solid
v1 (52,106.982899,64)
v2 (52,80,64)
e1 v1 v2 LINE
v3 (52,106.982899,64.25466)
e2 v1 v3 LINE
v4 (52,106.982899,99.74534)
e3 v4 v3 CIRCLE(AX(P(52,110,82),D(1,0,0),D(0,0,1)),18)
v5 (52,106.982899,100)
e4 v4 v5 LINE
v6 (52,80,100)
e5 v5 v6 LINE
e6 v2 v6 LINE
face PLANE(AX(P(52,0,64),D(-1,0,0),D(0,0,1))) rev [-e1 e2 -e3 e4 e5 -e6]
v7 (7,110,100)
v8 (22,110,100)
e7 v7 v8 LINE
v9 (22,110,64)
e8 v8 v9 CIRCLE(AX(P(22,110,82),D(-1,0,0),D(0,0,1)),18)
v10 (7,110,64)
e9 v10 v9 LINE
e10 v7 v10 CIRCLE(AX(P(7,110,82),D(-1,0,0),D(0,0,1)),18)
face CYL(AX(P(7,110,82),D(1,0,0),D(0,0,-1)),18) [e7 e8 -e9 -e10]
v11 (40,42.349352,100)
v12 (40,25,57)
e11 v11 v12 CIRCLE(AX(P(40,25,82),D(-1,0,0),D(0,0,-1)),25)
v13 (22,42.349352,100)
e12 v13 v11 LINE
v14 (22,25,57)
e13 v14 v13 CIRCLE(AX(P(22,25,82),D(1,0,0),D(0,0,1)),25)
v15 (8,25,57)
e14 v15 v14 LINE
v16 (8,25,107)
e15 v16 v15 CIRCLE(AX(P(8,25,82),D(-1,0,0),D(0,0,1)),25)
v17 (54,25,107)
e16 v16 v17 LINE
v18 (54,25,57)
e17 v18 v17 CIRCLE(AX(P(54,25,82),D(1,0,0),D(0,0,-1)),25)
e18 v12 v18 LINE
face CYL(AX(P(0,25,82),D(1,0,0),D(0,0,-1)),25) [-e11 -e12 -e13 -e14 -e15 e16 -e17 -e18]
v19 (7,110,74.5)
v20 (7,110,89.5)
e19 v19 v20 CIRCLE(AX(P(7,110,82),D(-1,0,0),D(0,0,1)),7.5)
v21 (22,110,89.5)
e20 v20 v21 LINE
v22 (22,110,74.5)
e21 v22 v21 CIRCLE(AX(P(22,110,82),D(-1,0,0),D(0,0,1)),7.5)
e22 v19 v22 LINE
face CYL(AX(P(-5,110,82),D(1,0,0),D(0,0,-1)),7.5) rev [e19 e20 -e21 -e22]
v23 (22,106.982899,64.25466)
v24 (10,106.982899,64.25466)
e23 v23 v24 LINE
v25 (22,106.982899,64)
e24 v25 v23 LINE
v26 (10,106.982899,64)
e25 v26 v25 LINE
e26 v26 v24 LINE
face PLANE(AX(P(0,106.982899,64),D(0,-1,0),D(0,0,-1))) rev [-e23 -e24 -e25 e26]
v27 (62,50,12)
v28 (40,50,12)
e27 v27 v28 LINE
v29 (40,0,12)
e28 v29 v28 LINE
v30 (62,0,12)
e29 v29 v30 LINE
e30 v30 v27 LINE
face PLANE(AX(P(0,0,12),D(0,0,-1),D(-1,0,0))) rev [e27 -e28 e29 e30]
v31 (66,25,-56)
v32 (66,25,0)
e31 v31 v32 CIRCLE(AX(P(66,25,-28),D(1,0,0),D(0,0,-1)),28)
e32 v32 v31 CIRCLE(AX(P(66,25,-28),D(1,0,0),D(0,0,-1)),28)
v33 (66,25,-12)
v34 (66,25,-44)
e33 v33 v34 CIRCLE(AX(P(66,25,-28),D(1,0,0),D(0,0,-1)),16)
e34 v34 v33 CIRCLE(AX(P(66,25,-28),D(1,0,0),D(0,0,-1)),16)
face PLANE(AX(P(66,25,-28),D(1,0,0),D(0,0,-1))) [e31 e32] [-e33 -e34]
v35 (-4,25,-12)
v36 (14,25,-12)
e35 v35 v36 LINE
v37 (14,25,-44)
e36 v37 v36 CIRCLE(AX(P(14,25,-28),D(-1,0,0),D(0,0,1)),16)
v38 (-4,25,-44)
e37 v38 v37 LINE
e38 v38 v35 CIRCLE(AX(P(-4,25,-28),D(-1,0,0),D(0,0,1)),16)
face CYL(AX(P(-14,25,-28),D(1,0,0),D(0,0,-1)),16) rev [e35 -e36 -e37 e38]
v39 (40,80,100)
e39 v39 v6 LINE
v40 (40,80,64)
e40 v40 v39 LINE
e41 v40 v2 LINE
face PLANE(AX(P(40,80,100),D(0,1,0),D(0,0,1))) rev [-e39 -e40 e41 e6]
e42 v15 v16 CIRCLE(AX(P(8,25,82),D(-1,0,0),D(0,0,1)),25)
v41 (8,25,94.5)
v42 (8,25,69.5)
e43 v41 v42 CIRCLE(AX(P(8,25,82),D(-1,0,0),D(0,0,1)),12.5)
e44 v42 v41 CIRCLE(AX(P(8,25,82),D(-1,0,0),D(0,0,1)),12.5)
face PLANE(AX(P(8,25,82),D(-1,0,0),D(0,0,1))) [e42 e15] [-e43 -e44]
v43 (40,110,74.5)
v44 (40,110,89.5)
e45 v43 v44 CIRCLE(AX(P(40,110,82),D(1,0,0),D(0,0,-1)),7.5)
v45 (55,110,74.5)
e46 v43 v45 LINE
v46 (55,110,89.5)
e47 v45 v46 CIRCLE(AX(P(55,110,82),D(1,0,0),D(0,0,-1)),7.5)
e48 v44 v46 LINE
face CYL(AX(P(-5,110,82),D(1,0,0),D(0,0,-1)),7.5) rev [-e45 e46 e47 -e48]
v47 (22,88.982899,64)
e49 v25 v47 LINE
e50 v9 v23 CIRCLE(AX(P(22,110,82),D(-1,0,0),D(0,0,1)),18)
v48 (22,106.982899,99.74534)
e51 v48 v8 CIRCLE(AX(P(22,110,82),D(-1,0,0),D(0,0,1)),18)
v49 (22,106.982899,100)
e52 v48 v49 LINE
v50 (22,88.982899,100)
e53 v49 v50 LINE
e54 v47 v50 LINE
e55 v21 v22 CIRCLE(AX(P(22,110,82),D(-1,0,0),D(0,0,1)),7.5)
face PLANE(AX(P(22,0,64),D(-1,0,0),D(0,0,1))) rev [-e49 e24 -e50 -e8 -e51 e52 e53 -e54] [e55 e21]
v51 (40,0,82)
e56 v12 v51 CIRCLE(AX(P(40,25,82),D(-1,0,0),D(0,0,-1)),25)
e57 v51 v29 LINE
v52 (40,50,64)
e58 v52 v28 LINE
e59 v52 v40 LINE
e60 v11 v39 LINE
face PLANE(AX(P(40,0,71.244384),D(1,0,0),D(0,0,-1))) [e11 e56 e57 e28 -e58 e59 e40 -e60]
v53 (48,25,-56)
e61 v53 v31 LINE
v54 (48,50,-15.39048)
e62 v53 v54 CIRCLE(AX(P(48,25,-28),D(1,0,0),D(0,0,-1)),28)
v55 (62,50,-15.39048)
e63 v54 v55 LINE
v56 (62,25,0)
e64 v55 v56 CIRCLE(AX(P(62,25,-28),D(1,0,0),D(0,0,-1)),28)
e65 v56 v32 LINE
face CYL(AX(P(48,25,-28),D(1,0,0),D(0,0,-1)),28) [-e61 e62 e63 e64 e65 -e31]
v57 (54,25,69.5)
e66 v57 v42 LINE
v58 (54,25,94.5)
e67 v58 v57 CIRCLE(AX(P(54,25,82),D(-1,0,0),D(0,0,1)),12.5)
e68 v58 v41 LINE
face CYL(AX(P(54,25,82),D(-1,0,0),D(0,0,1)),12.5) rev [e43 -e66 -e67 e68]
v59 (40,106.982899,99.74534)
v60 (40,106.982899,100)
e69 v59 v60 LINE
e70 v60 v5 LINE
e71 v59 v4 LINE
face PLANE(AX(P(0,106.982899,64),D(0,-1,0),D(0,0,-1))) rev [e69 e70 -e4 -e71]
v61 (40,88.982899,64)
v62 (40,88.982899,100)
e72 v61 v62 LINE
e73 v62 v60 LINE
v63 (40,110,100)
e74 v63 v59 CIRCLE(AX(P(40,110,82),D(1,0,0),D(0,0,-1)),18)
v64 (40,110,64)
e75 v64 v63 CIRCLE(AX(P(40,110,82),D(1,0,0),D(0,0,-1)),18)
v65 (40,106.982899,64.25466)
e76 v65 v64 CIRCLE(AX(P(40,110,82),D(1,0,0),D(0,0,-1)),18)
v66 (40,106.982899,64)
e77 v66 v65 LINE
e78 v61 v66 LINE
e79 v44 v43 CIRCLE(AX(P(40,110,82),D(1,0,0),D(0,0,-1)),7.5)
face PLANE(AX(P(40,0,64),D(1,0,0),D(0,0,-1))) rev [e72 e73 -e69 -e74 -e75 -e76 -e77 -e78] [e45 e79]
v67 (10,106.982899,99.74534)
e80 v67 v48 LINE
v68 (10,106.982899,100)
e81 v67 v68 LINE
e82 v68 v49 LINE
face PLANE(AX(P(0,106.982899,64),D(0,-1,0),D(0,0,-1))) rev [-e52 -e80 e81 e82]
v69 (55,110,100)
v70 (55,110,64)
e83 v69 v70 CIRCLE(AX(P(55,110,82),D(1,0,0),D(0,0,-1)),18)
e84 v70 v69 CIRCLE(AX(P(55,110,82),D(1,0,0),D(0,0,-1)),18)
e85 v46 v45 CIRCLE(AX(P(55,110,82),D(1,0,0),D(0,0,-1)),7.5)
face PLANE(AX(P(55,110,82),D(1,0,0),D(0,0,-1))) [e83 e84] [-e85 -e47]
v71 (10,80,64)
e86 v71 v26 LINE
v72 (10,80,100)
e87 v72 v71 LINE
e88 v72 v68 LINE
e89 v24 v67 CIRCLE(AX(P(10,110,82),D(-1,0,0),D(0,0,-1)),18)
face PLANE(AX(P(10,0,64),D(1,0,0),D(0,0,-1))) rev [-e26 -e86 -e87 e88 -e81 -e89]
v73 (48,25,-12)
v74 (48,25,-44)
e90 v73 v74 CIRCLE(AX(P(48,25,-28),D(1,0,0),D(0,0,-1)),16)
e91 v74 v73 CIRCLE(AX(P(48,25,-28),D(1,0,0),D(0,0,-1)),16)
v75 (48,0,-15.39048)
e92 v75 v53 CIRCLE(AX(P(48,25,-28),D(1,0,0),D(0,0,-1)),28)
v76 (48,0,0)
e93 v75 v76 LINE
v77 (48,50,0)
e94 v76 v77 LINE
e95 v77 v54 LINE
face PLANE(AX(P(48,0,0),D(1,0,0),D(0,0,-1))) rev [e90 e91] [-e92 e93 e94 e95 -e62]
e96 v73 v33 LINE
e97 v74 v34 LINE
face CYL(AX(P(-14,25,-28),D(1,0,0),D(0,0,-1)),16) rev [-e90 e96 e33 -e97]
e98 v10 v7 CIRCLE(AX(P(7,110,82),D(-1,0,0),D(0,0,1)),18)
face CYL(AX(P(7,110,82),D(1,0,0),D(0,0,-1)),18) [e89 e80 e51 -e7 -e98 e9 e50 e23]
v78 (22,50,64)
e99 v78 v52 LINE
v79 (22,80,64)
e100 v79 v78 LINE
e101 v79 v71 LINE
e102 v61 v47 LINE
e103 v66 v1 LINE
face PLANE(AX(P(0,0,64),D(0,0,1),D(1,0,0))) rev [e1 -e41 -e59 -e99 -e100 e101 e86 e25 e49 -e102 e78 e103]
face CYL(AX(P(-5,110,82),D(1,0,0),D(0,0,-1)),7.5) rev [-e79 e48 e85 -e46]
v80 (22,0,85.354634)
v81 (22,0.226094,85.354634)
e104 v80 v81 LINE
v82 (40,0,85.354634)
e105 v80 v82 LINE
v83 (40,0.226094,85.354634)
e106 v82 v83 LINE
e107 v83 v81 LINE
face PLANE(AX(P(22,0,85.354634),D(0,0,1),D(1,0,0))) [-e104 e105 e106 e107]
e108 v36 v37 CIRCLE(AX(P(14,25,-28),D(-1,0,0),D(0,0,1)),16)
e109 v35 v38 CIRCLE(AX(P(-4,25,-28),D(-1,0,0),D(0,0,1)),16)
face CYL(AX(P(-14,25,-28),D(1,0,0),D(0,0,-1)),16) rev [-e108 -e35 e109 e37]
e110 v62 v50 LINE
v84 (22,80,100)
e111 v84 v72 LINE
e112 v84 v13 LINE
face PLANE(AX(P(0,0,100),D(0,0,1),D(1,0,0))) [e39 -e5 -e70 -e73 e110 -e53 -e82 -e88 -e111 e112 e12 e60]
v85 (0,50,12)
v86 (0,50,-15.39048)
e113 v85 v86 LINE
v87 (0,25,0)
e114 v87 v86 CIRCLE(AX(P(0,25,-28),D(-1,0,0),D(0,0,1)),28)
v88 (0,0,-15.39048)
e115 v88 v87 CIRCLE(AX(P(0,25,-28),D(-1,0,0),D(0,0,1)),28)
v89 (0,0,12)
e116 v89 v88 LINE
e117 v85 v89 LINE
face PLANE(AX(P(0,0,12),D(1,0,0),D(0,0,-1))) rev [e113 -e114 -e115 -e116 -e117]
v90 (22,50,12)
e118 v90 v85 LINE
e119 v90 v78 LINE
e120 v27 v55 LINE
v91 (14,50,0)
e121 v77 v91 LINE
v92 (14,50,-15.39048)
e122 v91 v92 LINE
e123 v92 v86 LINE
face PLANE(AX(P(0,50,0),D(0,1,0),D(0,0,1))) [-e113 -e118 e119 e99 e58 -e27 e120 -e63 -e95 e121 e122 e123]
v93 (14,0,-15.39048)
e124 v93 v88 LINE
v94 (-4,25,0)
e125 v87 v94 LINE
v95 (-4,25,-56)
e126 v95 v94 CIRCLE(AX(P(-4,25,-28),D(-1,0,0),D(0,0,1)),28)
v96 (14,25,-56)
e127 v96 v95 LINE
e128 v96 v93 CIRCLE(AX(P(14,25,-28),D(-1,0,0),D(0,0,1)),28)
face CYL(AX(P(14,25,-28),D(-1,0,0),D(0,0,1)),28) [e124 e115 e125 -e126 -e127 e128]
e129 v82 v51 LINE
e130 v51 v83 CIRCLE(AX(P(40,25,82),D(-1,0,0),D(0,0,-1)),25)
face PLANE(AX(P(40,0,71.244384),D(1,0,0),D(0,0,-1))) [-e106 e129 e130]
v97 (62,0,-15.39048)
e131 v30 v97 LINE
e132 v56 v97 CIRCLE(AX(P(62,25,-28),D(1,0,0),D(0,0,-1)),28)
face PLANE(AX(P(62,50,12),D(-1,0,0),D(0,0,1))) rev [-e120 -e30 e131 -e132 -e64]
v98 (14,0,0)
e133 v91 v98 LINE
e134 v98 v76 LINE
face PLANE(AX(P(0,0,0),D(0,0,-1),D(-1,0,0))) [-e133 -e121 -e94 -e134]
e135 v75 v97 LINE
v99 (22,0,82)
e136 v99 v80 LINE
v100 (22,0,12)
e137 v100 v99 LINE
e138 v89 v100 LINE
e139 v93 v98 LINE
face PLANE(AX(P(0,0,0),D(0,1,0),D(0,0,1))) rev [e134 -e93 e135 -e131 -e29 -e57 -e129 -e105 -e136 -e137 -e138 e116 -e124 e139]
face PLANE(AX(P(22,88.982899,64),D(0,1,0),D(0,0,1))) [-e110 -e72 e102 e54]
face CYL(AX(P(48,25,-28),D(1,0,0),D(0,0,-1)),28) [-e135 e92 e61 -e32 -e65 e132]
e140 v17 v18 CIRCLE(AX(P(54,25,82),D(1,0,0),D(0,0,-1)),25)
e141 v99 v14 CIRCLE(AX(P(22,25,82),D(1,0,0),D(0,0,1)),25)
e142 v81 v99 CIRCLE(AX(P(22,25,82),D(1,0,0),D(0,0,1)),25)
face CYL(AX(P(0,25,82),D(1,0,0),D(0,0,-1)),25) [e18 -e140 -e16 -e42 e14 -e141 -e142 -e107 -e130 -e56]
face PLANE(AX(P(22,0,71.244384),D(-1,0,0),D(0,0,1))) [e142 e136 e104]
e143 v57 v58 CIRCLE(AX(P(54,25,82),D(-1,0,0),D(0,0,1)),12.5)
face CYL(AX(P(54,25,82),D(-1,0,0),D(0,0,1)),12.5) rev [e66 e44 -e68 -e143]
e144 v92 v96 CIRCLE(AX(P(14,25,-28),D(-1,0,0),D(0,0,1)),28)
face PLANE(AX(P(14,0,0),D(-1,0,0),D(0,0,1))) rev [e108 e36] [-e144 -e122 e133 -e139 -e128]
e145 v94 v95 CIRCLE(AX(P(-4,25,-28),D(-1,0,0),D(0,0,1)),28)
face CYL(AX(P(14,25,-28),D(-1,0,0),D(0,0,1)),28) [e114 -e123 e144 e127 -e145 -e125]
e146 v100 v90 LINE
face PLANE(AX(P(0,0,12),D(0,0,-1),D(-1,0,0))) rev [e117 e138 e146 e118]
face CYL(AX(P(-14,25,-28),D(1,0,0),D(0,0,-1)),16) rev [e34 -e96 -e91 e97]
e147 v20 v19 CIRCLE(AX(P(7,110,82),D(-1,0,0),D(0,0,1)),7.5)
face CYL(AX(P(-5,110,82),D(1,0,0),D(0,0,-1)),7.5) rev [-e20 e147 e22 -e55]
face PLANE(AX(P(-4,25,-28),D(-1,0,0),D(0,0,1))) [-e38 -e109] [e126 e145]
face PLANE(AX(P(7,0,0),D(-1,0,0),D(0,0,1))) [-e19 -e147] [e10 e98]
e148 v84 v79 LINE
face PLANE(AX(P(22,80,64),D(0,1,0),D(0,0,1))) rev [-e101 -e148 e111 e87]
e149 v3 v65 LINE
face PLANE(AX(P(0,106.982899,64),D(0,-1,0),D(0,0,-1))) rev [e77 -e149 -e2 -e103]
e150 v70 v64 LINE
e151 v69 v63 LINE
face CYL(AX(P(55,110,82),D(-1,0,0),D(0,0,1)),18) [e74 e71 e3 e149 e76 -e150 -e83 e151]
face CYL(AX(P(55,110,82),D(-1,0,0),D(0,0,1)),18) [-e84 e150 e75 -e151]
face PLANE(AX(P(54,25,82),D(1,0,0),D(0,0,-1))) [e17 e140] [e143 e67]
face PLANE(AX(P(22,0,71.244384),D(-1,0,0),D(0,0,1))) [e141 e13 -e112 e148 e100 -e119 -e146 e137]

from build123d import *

# Parameters (mm, degrees)
BASE_PLATE_DEPTH                = 12
EYE_BOSS_A_SKETCH_R             = 28
EYE_BOSS_A_56_DEPTH             = 14
EYE_HUB_A_SKETCH_R              = 28
EYE_HUB_A_56X4_DEPTH            = 4
EYE_WEB_A_DEPTH                 = 14
EYE_START                       = -14
EYE_BOSS_B_SKETCH_R             = 28
EYE_BOSS_B_DEPTH                = 14
EYE_HUB_B_SKETCH_R              = 28
EYE_HUB_B_56X4_DEPTH            = 4
SIDE_BOSS_SKETCH_R              = 25
SIDE_BOSS_50_DEPTH              = 62
SIDE_BOSS_FACE_CUT_A_SKETCH_R   = 25
SIDE_BOSS_FACE_CUT_A_50X8_DEPTH = 8
SIDE_BOSS_FACE_CUT_B_SKETCH_R   = 25
SIDE_BOSS_FACE_CUT_B_50X8_DEPTH = 8
SIDE_BORE_SKETCH_R              = 12.5
SIDE_BORE_25_DEPTH              = 46
EYE_BORE_SKETCH_R               = 16
EYE_BORE_32_DEPTH               = 80
CENTRAL_BODY_DEPTH              = 50
BODY_START                      = -50
BODY_SLOT_CUT_DEPTH             = 50
UPPER_LUG_A_SKETCH_R            = 18
UPPER_LUG_A_36_DEPTH            = 15
UPPER_LUG_B_SKETCH_R            = 18
UPPER_LUG_B_36_DEPTH            = 15
UPPER_CLEVIS_BODY_DEPTH         = 36
UPPER_CLEVIS_INFILL_SKETCH_W    = 18
UPPER_CLEVIS_INFILL_SKETCH_H    = 12
UPPER_CLEVIS_INFILL_DEPTH       = 36
CLEVIS_SLOT_A_SKETCH_W          = 36
CLEVIS_SLOT_A_SKETCH_H          = 18
CLEVIS_SLOT_A_DEPTH             = 12
CLEVIS_SLOT_B_SKETCH_W          = 36
CLEVIS_SLOT_B_SKETCH_H          = 18
CLEVIS_SLOT_B_DEPTH             = 12
LUG_PIN_HOLE_SKETCH_R           = 7.5
LUG_PIN_HOLE_15_DEPTH           = 60
SIDE_SLOT_CUT_DEPTH             = 60


with BuildPart() as part:
    # Base Plate Sketch → Base Plate (new body)
    with BuildSketch(Plane.XY):
        Polygon((0, 0), (14, 0), (48, 0), (62, 0), (62, 50), (0, 50), align=None)
    extrude(amount=BASE_PLATE_DEPTH)



with BuildPart() as body_2:
    # Eye Boss A Sketch → Eye Boss A _56 (new body)
    with BuildSketch(Plane(origin=(62, 0, 0), x_dir=(0, 0, -1), z_dir=(1, 0, 0))):
        with Locations((28, 25)):
            Circle(EYE_BOSS_A_SKETCH_R)
    extrude(amount=-EYE_BOSS_A_56_DEPTH)

    # Eye Hub A Sketch → Eye Hub A _56x4 (add)
    with BuildSketch(Plane(origin=(62, 0, 0), x_dir=(0, 0, -1), z_dir=(1, 0, 0))):
        with Locations((28, 25)):
            Circle(EYE_HUB_A_SKETCH_R)
    extrude(amount=EYE_HUB_A_56X4_DEPTH)


with BuildPart() as part_1:
    add(part.part)

    add(body_2.part)  # Eye Web A merges body 2
    # Eye Web A Sketch → Eye Web A (add)
    with BuildSketch(Plane(origin=(62, 0, 0), x_dir=(0, 0, -1), z_dir=(1, 0, 0))):
        with BuildLine():
            Line((15.390479787, 50), (0, 50))
            Line((0, 50), (0, 25.000000117))
            ThreePointArc((0, 25.000000117), (4.156064051, 39.678784639), (15.390479787, 50))
        make_face()
        with BuildLine():
            ThreePointArc((15.390479787, 0), (4.15606399, 10.32121546), (0, 25.000000117))
            Line((0, 25.000000117), (0, 0))
            Line((0, 0), (15.390479787, 0))
        make_face()
    extrude(amount=-EYE_WEB_A_DEPTH)

    # Eye Boss B Sketch → Eye Boss B (add)
    with BuildSketch(Plane.ZY.offset(EYE_START)):
        with Locations(Location((-28, 25, 0), (0, 0, 180))):
            Circle(EYE_BOSS_B_SKETCH_R)
        with BuildLine():
            Line((0, 25), (0, 50))
            Line((0, 50), (-15.390479787, 50))
            ThreePointArc((-15.390479787, 50), (-4.156064021, 39.678784589), (0, 25))
        make_face()
        with BuildLine():
            Line((0, 0), (0, 25))
            ThreePointArc((0, 25), (-4.156064021, 10.321215411), (-15.390479787, 0))
            Line((-15.390479787, 0), (0, 0))
        make_face()
    extrude(amount=EYE_BOSS_B_DEPTH)

    # Eye Hub B Sketch → Eye Hub B _56x4 (add)
    with BuildSketch(Plane.ZY):
        with Locations(Location((-28, 25, 0), (0, 0, 180))):
            Circle(EYE_HUB_B_SKETCH_R)
    extrude(amount=EYE_HUB_B_56X4_DEPTH)

    # Eye Bore Sketch → Eye Bore _32 (cut)
    with BuildSketch(Plane(origin=(66, 0, 0), x_dir=(0, 0, -1), z_dir=(1, 0, 0))):
        with Locations(Location((28, 25, 0), (0, 0, 180))):
            Circle(EYE_BORE_SKETCH_R)
    extrude(amount=-EYE_BORE_32_DEPTH, mode=Mode.SUBTRACT)



with BuildPart() as body_2_2:
    # Side Boss Sketch → Side Boss _50 (new body)
    with BuildSketch(Plane(origin=(62, 0, 0), x_dir=(0, 0, -1), z_dir=(1, 0, 0))):
        with Locations((-82, 25)):
            Circle(SIDE_BOSS_SKETCH_R)
    extrude(amount=-SIDE_BOSS_50_DEPTH)

    # Side Boss Face Cut A Sketch → Side Boss Face Cut A _50x8 (cut)
    with BuildSketch(Plane(origin=(62, 0, 0), x_dir=(0, 0, -1), z_dir=(1, 0, 0))):
        with Locations((-82, 25)):
            Circle(SIDE_BOSS_FACE_CUT_A_SKETCH_R)
    extrude(amount=-SIDE_BOSS_FACE_CUT_A_50X8_DEPTH, mode=Mode.SUBTRACT)

    # Side Boss Face Cut B Sketch → Side Boss Face Cut B _50x8 (cut)
    with BuildSketch(Plane.ZY):
        with Locations(Location((82, 25, 0), (0, 0, 180))):
            Circle(SIDE_BOSS_FACE_CUT_B_SKETCH_R)
    extrude(amount=-SIDE_BOSS_FACE_CUT_B_50X8_DEPTH, mode=Mode.SUBTRACT)

    # Side Bore Sketch → Side Bore _25 (cut)
    with BuildSketch(Plane.ZY.offset(-8)):
        with Locations((82, 25)):
            Circle(SIDE_BORE_SKETCH_R)
    extrude(amount=-SIDE_BORE_25_DEPTH, mode=Mode.SUBTRACT)


with BuildPart() as part_2:
    add(part_1.part)

    add(body_2_2.part)  # Central Body merges body 2 2
    # Central Body Sketch → Central Body (add)
    with BuildSketch(Plane(origin=(0, 50, 0), x_dir=(1, 0, 0), z_dir=(0, 1, 0))):
        Polygon((31, -12), (22, -12), (22, -71.244384349), (22, -85.354634245), (40, -85.354634245), (40, -71.244384349), (40, -12), align=None)
    extrude(amount=-CENTRAL_BODY_DEPTH)

    # Body Slot Sketch → Body Slot Cut (cut)
    with BuildSketch(Plane(origin=(40, 0, 0), x_dir=(0, 0, -1), z_dir=(1, 0, 0)).offset(BODY_START)):
        with BuildLine():
            Line((-85.354634245, 37.041446303), (-85.354634245, 12.958553697))
            ThreePointArc((-85.354634245, 12.958553697), (-69.5, 25), (-85.354634245, 37.041446303))
        make_face()
    extrude(amount=BODY_SLOT_CUT_DEPTH, mode=Mode.SUBTRACT)



with BuildPart() as body_2_3:
    # Upper Lug A Sketch → Upper Lug A _36 (new body)
    with BuildSketch(Plane.ZY.offset(-22)):
        with Locations((82, 110)):
            Circle(UPPER_LUG_A_SKETCH_R)
    extrude(amount=UPPER_LUG_A_36_DEPTH)


with BuildPart() as body_3:
    # Upper Lug B Sketch → Upper Lug B _36 (new body)
    with BuildSketch(Plane(origin=(40, 0, 0), x_dir=(0, 0, -1), z_dir=(1, 0, 0))):
        with Locations((-82, 110)):
            Circle(UPPER_LUG_B_SKETCH_R)
    extrude(amount=UPPER_LUG_B_36_DEPTH)


with BuildPart() as part_3:
    add(part_2.part)

    add(body_2_3.part)  # Upper Clevis Body merges body 2 3

    add(body_3.part)  # Upper Clevis Body merges body 3
    # Upper Clevis Profile Sketch → Upper Clevis Body (add)
    with BuildSketch(Plane.XY.offset(100)):
        Polygon((22, 62), (22, 49.773906214), (22, 25.080522604), (40, 25.080522604), (40, 50), (40, 62), (52, 62), (52, 92), (52, 106.982899018), (40, 106.982899018), (40, 76.982899018), (22, 76.982899018), (22, 106.982899018), (10, 106.982899018), (10, 92), (10, 62), align=None)
    extrude(amount=-UPPER_CLEVIS_BODY_DEPTH)

    # Upper Clevis Infill Sketch → Upper Clevis Infill (add)
    with BuildSketch(Plane.XY.offset(100)):
        with Locations((31, 82.982899018)):
            Rectangle(UPPER_CLEVIS_INFILL_SKETCH_W, UPPER_CLEVIS_INFILL_SKETCH_H)
    extrude(amount=-UPPER_CLEVIS_INFILL_DEPTH)

    # Clevis Slot A Sketch → Clevis Slot A (cut)
    with BuildSketch(Plane(origin=(52, 0, 0), x_dir=(0, 0, -1), z_dir=(1, 0, 0))):
        with Locations((-82, 71)):
            Rectangle(CLEVIS_SLOT_A_SKETCH_W, CLEVIS_SLOT_A_SKETCH_H)
    extrude(amount=-CLEVIS_SLOT_A_DEPTH, mode=Mode.SUBTRACT)

    # Clevis Slot B Sketch → Clevis Slot B (cut)
    with BuildSketch(Plane.ZY.offset(-10)):
        with Locations((82, 71)):
            Rectangle(CLEVIS_SLOT_B_SKETCH_W, CLEVIS_SLOT_B_SKETCH_H)
    extrude(amount=-CLEVIS_SLOT_B_DEPTH, mode=Mode.SUBTRACT)

    # Lug Pin Hole Sketch → Lug Pin Hole _15 (cut)
    with BuildSketch(Plane(origin=(55, 0, 0), x_dir=(0, 0, -1), z_dir=(1, 0, 0))):
        with Locations((-82, 110)):
            Circle(LUG_PIN_HOLE_SKETCH_R)
    extrude(amount=-LUG_PIN_HOLE_15_DEPTH, mode=Mode.SUBTRACT)

    # Side Slot Sketch → Side Slot Cut (cut)
    with BuildSketch(Plane.ZY.offset(-22)):
        with BuildLine():
            Line((69.5, 25), (94.5, 25))
            ThreePointArc((94.5, 25), (82, 37.5), (69.5, 25))
        make_face()
    extrude(amount=-SIDE_SLOT_CUT_DEPTH, mode=Mode.SUBTRACT)


solid = part_3.part
